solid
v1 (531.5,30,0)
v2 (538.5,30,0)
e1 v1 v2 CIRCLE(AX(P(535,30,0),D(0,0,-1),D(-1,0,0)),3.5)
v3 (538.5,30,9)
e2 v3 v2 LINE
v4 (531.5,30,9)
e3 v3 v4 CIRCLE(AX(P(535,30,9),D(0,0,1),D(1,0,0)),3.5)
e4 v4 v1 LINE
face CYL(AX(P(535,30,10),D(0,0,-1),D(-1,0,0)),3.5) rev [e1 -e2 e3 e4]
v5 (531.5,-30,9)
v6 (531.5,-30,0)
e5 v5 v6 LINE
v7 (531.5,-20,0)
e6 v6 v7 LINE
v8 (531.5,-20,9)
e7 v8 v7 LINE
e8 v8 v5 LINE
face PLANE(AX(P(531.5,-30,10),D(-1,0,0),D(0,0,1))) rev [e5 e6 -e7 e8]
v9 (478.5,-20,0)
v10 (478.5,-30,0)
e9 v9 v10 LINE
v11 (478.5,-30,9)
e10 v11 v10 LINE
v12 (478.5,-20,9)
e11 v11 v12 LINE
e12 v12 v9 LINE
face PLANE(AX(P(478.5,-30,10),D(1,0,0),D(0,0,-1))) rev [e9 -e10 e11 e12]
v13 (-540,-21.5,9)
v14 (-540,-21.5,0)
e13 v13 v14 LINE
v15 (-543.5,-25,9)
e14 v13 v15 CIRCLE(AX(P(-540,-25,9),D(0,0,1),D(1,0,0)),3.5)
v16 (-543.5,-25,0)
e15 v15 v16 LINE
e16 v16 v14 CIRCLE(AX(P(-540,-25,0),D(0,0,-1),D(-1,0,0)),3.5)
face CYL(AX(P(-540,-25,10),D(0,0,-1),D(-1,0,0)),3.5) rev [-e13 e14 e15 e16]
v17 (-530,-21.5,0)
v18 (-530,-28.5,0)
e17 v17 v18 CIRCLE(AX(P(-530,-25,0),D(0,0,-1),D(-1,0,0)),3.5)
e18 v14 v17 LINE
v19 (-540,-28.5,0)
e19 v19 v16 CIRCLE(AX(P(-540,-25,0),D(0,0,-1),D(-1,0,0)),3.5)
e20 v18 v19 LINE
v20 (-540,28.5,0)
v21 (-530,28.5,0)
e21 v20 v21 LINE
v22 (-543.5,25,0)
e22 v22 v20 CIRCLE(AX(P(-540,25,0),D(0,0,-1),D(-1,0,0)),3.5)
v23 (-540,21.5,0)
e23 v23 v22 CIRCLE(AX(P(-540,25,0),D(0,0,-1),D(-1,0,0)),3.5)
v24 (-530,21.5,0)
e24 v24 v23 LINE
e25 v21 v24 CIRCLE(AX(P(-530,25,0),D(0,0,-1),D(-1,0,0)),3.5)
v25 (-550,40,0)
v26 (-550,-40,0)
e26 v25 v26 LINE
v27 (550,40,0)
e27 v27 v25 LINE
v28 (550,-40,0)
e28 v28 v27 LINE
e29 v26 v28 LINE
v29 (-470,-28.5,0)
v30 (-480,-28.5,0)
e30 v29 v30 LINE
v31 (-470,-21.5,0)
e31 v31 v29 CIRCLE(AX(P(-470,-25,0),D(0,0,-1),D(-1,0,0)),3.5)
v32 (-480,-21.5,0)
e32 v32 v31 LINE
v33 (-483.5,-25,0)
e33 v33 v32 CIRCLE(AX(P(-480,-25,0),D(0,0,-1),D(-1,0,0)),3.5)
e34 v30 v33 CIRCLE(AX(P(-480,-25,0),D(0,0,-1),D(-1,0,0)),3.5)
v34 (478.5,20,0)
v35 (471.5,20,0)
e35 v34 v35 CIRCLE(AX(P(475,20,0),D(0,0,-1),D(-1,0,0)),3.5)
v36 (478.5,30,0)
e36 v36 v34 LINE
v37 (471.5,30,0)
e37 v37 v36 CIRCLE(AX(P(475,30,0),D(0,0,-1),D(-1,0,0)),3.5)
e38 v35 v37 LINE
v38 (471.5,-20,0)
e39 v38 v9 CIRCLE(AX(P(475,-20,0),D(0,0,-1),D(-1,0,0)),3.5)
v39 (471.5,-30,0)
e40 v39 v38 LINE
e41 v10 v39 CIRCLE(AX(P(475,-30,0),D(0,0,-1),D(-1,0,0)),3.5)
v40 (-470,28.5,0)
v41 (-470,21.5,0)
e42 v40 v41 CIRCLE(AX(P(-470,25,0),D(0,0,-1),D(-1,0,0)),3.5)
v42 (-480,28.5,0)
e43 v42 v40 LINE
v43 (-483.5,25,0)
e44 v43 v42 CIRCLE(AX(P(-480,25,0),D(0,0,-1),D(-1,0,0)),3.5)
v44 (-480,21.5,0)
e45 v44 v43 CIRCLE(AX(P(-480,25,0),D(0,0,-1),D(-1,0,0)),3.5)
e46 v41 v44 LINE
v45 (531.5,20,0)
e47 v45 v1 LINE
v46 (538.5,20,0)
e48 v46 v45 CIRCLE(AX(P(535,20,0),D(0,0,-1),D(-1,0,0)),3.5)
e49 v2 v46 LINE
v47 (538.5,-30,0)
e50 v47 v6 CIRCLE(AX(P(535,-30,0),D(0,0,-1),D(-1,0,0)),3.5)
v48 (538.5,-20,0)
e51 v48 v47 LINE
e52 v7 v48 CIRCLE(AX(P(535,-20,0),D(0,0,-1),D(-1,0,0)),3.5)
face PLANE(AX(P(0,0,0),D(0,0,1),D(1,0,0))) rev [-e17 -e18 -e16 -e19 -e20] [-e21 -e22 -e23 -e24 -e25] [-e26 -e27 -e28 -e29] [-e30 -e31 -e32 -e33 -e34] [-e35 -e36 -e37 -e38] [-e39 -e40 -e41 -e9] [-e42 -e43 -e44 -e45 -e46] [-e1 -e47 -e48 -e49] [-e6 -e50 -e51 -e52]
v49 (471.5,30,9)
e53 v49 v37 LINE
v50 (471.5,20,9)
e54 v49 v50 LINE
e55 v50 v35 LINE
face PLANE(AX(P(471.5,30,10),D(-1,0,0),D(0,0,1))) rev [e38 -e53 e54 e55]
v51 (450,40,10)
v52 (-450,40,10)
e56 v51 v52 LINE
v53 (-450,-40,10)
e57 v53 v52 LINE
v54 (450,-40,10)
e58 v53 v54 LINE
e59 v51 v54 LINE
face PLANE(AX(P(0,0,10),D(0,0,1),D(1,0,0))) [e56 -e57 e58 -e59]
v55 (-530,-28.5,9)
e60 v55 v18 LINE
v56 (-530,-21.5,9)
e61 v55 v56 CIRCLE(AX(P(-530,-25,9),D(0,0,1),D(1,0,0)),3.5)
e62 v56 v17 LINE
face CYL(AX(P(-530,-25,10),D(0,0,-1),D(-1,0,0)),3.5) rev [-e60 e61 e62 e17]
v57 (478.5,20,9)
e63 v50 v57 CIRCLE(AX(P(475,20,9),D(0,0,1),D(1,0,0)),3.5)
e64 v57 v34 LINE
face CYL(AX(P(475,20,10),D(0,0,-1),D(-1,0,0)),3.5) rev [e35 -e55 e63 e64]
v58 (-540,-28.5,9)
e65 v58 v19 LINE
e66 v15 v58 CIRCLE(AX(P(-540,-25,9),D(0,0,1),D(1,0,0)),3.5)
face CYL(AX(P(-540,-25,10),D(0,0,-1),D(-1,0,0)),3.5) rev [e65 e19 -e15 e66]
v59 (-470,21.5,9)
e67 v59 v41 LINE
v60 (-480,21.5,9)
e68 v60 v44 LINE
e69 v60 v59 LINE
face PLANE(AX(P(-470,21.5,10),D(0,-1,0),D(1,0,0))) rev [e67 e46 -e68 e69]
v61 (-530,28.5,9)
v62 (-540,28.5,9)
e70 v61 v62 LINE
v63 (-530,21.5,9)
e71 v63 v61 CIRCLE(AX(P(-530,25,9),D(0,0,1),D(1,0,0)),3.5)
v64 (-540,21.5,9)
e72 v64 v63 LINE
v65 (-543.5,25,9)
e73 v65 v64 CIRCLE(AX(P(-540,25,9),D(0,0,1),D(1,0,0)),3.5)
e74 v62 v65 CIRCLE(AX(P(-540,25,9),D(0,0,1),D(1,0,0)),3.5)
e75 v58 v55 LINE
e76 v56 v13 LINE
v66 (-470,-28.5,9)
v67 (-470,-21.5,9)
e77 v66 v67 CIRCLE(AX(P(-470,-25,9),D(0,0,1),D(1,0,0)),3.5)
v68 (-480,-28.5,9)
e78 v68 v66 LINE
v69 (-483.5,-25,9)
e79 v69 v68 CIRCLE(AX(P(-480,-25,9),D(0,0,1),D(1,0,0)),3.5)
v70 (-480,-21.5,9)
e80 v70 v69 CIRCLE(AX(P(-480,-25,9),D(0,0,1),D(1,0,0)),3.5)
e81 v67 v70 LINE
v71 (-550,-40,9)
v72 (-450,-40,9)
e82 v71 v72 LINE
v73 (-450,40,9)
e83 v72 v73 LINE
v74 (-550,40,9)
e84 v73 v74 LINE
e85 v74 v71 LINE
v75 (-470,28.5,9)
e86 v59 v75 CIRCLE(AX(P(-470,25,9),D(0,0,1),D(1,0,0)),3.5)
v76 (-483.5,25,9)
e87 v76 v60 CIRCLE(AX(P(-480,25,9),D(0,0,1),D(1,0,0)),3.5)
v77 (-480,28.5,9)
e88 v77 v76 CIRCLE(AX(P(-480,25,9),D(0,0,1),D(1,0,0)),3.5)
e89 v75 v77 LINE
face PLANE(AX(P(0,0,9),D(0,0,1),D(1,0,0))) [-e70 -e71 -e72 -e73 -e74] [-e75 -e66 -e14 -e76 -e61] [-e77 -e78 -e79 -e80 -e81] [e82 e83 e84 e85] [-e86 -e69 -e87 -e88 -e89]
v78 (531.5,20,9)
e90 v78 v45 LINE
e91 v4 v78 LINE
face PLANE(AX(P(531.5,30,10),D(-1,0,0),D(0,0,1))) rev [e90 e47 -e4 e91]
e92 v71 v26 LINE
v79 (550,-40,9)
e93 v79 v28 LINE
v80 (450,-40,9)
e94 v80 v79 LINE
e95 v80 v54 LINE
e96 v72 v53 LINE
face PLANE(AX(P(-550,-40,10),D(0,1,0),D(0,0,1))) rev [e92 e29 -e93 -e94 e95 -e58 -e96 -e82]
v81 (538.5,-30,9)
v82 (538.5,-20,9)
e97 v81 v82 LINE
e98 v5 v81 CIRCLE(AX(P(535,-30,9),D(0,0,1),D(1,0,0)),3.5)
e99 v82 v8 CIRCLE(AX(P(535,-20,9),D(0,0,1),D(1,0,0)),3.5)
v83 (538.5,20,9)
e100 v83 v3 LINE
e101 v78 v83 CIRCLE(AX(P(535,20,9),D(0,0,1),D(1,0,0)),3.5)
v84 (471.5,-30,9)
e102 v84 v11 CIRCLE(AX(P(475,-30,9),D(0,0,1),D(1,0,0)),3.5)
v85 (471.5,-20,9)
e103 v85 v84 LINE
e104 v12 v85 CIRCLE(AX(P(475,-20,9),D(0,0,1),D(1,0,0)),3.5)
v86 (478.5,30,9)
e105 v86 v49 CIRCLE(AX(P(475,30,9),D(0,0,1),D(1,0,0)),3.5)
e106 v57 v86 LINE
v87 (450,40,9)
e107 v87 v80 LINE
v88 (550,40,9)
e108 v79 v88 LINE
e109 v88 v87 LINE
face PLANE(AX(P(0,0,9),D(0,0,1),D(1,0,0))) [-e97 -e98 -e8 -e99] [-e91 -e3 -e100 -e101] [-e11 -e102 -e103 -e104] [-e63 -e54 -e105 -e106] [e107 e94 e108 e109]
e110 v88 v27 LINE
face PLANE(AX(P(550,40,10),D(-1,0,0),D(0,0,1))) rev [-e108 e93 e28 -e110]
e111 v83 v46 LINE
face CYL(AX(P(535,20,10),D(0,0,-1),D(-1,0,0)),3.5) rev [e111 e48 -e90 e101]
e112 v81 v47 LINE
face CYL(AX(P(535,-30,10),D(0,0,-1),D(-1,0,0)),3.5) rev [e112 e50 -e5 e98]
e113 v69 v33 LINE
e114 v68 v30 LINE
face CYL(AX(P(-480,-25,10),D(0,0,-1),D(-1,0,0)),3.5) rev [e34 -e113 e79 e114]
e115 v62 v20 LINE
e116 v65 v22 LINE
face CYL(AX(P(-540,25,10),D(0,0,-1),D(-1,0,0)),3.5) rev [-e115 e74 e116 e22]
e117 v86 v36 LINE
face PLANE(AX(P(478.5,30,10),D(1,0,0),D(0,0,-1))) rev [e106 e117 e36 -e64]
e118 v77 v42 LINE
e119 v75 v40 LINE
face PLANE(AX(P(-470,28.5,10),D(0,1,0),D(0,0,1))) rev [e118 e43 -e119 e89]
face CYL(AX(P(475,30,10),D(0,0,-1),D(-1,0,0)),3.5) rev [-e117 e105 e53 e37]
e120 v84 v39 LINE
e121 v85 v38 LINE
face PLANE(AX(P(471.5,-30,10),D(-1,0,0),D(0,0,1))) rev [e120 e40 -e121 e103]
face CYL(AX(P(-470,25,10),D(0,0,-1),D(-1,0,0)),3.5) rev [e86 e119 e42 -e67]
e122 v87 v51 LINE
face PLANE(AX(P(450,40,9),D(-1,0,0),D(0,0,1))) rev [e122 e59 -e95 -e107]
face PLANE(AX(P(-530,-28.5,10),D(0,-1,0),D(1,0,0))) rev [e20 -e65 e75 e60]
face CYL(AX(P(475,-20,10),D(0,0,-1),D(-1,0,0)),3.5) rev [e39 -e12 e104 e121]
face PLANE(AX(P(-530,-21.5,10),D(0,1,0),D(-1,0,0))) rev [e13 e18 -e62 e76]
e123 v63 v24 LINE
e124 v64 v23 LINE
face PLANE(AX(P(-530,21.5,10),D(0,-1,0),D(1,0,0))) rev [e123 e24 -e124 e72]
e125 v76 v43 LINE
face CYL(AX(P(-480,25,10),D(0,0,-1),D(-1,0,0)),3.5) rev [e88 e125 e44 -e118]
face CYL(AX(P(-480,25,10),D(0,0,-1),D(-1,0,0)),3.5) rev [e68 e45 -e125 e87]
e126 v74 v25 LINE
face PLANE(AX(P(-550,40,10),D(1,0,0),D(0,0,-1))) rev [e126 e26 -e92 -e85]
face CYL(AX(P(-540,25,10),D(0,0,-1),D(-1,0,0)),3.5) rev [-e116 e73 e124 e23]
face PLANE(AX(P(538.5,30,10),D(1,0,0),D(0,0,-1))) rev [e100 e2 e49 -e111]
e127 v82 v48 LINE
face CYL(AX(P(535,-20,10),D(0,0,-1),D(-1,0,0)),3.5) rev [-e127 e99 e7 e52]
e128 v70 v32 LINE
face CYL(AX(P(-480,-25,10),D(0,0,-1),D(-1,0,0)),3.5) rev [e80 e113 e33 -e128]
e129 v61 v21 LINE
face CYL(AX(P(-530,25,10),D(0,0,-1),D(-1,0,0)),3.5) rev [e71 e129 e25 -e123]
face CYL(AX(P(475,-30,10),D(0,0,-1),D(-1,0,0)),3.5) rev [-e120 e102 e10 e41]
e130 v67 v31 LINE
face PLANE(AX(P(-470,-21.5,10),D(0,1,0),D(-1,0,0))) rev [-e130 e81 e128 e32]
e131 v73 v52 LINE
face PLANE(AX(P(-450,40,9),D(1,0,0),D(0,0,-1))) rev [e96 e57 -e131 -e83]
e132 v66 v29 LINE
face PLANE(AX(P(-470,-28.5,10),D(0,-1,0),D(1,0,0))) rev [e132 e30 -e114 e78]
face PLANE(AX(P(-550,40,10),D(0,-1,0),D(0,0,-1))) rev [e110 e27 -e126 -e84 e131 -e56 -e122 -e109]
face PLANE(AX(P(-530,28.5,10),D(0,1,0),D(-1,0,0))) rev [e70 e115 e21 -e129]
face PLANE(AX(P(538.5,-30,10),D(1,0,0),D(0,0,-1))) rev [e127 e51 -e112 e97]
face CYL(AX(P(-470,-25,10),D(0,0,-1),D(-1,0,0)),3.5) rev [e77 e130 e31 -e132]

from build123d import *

# Parameters (mm, degrees)
SKETCH_1_W             = 1100
SKETCH_1_H             = 80
EXTRUDE_1_DEPTH        = 10
SKETCH_2_W             = 100
SKETCH_2_H             = 80
CUT_EXTRUDE_1_DEPTH    = 1
HOLE_WIZARD_M6_1_D     = 7
HOLE_WIZARD_M6_1_DEPTH = 22.25
HOLE_WIZARD_M6_1_TIP   = 2.103012167
CUT_EXTRUDE_2_DEPTH    = 552.543289326


with BuildPart() as part:
    # 草图1 → 凸台-拉伸1 (new body)
    with BuildSketch(Plane.XY):
        Rectangle(SKETCH_1_W, SKETCH_1_H)
    extrude(amount=EXTRUDE_1_DEPTH)

    # 草图2 → 切除-拉伸1 (cut)
    with BuildSketch(Plane.XY.offset(10)):
        with Locations((-500, 0)):
            Rectangle(SKETCH_2_W, SKETCH_2_H)
        with Locations((500, 0)):
            Rectangle(SKETCH_2_W, SKETCH_2_H)
    extrude(amount=-CUT_EXTRUDE_1_DEPTH, mode=Mode.SUBTRACT)

    # M6 间隙孔1
    with Locations(Plane(origin=(0, 0, 0), x_dir=(-1, 0, 0), z_dir=(0, 0, -1))):
        with Locations((-535, 25), (475, -25), (535, 25), (535, -25), (475, 25), (-475, 25), (-475, -25), (-535, -25)):
            Hole(HOLE_WIZARD_M6_1_D / 2, depth=HOLE_WIZARD_M6_1_DEPTH)
            with Locations((0, 0, -(HOLE_WIZARD_M6_1_DEPTH + HOLE_WIZARD_M6_1_TIP / 2))):  # 118° drill point
                Cone(0, HOLE_WIZARD_M6_1_D / 2, HOLE_WIZARD_M6_1_TIP, mode=Mode.SUBTRACT)

    # 草图5 → 切除-拉伸2 (cut, through all)
    with BuildSketch(Plane(origin=(0, 0, 0), x_dir=(-1, 0, 0), z_dir=(0, 0, -1))):
        with BuildLine():
            Line((470, 28.5), (480, 28.5))
            ThreePointArc((480, 28.5), (483.5, 25), (480, 21.5))
            Line((480, 21.5), (470, 21.5))
            ThreePointArc((470, 21.5), (466.5, 25), (470, 28.5))
        make_face()
        with BuildLine():
            Line((530, 28.5), (540, 28.5))
            ThreePointArc((540, 28.5), (543.5, 25), (540, 21.5))
            Line((540, 21.5), (530, 21.5))
            ThreePointArc((530, 21.5), (526.5, 25), (530, 28.5))
        make_face()
        with BuildLine():
            Line((530, -21.5), (540, -21.5))
            ThreePointArc((540, -21.5), (543.5, -25), (540, -28.5))
            Line((540, -28.5), (530, -28.5))
            ThreePointArc((530, -28.5), (526.5, -25), (530, -21.5))
        make_face()
        with BuildLine():
            Line((470, -21.5), (480, -21.5))
            ThreePointArc((480, -21.5), (483.5, -25), (480, -28.5))
            Line((480, -28.5), (470, -28.5))
            ThreePointArc((470, -28.5), (466.5, -25), (470, -21.5))
        make_face()
        with BuildLine():
            Line((-531.5, 30), (-531.5, 20))
            ThreePointArc((-531.5, 20), (-535, 16.5), (-538.5, 20))
            Line((-538.5, 20), (-538.5, 30))
            ThreePointArc((-538.5, 30), (-535, 33.5), (-531.5, 30))
        make_face()
        with BuildLine():
            Line((-471.5, 30), (-471.5, 20))
            ThreePointArc((-471.5, 20), (-475, 16.5), (-478.5, 20))
            Line((-478.5, 20), (-478.5, 30))
            ThreePointArc((-478.5, 30), (-475, 33.5), (-471.5, 30))
        make_face()
        with BuildLine():
            Line((-538.5, -30), (-538.5, -20))
            ThreePointArc((-538.5, -20), (-535, -16.5), (-531.5, -20))
            Line((-531.5, -20), (-531.5, -30))
            ThreePointArc((-531.5, -30), (-535, -33.5), (-538.5, -30))
        make_face()
        with BuildLine():
            Line((-478.5, -30), (-478.5, -20))
            ThreePointArc((-478.5, -20), (-475, -16.5), (-471.5, -20))
            Line((-471.5, -20), (-471.5, -30))
            ThreePointArc((-471.5, -30), (-475, -33.5), (-478.5, -30))
        make_face()
    extrude(amount=-CUT_EXTRUDE_2_DEPTH, mode=Mode.SUBTRACT)


solid = part.part
